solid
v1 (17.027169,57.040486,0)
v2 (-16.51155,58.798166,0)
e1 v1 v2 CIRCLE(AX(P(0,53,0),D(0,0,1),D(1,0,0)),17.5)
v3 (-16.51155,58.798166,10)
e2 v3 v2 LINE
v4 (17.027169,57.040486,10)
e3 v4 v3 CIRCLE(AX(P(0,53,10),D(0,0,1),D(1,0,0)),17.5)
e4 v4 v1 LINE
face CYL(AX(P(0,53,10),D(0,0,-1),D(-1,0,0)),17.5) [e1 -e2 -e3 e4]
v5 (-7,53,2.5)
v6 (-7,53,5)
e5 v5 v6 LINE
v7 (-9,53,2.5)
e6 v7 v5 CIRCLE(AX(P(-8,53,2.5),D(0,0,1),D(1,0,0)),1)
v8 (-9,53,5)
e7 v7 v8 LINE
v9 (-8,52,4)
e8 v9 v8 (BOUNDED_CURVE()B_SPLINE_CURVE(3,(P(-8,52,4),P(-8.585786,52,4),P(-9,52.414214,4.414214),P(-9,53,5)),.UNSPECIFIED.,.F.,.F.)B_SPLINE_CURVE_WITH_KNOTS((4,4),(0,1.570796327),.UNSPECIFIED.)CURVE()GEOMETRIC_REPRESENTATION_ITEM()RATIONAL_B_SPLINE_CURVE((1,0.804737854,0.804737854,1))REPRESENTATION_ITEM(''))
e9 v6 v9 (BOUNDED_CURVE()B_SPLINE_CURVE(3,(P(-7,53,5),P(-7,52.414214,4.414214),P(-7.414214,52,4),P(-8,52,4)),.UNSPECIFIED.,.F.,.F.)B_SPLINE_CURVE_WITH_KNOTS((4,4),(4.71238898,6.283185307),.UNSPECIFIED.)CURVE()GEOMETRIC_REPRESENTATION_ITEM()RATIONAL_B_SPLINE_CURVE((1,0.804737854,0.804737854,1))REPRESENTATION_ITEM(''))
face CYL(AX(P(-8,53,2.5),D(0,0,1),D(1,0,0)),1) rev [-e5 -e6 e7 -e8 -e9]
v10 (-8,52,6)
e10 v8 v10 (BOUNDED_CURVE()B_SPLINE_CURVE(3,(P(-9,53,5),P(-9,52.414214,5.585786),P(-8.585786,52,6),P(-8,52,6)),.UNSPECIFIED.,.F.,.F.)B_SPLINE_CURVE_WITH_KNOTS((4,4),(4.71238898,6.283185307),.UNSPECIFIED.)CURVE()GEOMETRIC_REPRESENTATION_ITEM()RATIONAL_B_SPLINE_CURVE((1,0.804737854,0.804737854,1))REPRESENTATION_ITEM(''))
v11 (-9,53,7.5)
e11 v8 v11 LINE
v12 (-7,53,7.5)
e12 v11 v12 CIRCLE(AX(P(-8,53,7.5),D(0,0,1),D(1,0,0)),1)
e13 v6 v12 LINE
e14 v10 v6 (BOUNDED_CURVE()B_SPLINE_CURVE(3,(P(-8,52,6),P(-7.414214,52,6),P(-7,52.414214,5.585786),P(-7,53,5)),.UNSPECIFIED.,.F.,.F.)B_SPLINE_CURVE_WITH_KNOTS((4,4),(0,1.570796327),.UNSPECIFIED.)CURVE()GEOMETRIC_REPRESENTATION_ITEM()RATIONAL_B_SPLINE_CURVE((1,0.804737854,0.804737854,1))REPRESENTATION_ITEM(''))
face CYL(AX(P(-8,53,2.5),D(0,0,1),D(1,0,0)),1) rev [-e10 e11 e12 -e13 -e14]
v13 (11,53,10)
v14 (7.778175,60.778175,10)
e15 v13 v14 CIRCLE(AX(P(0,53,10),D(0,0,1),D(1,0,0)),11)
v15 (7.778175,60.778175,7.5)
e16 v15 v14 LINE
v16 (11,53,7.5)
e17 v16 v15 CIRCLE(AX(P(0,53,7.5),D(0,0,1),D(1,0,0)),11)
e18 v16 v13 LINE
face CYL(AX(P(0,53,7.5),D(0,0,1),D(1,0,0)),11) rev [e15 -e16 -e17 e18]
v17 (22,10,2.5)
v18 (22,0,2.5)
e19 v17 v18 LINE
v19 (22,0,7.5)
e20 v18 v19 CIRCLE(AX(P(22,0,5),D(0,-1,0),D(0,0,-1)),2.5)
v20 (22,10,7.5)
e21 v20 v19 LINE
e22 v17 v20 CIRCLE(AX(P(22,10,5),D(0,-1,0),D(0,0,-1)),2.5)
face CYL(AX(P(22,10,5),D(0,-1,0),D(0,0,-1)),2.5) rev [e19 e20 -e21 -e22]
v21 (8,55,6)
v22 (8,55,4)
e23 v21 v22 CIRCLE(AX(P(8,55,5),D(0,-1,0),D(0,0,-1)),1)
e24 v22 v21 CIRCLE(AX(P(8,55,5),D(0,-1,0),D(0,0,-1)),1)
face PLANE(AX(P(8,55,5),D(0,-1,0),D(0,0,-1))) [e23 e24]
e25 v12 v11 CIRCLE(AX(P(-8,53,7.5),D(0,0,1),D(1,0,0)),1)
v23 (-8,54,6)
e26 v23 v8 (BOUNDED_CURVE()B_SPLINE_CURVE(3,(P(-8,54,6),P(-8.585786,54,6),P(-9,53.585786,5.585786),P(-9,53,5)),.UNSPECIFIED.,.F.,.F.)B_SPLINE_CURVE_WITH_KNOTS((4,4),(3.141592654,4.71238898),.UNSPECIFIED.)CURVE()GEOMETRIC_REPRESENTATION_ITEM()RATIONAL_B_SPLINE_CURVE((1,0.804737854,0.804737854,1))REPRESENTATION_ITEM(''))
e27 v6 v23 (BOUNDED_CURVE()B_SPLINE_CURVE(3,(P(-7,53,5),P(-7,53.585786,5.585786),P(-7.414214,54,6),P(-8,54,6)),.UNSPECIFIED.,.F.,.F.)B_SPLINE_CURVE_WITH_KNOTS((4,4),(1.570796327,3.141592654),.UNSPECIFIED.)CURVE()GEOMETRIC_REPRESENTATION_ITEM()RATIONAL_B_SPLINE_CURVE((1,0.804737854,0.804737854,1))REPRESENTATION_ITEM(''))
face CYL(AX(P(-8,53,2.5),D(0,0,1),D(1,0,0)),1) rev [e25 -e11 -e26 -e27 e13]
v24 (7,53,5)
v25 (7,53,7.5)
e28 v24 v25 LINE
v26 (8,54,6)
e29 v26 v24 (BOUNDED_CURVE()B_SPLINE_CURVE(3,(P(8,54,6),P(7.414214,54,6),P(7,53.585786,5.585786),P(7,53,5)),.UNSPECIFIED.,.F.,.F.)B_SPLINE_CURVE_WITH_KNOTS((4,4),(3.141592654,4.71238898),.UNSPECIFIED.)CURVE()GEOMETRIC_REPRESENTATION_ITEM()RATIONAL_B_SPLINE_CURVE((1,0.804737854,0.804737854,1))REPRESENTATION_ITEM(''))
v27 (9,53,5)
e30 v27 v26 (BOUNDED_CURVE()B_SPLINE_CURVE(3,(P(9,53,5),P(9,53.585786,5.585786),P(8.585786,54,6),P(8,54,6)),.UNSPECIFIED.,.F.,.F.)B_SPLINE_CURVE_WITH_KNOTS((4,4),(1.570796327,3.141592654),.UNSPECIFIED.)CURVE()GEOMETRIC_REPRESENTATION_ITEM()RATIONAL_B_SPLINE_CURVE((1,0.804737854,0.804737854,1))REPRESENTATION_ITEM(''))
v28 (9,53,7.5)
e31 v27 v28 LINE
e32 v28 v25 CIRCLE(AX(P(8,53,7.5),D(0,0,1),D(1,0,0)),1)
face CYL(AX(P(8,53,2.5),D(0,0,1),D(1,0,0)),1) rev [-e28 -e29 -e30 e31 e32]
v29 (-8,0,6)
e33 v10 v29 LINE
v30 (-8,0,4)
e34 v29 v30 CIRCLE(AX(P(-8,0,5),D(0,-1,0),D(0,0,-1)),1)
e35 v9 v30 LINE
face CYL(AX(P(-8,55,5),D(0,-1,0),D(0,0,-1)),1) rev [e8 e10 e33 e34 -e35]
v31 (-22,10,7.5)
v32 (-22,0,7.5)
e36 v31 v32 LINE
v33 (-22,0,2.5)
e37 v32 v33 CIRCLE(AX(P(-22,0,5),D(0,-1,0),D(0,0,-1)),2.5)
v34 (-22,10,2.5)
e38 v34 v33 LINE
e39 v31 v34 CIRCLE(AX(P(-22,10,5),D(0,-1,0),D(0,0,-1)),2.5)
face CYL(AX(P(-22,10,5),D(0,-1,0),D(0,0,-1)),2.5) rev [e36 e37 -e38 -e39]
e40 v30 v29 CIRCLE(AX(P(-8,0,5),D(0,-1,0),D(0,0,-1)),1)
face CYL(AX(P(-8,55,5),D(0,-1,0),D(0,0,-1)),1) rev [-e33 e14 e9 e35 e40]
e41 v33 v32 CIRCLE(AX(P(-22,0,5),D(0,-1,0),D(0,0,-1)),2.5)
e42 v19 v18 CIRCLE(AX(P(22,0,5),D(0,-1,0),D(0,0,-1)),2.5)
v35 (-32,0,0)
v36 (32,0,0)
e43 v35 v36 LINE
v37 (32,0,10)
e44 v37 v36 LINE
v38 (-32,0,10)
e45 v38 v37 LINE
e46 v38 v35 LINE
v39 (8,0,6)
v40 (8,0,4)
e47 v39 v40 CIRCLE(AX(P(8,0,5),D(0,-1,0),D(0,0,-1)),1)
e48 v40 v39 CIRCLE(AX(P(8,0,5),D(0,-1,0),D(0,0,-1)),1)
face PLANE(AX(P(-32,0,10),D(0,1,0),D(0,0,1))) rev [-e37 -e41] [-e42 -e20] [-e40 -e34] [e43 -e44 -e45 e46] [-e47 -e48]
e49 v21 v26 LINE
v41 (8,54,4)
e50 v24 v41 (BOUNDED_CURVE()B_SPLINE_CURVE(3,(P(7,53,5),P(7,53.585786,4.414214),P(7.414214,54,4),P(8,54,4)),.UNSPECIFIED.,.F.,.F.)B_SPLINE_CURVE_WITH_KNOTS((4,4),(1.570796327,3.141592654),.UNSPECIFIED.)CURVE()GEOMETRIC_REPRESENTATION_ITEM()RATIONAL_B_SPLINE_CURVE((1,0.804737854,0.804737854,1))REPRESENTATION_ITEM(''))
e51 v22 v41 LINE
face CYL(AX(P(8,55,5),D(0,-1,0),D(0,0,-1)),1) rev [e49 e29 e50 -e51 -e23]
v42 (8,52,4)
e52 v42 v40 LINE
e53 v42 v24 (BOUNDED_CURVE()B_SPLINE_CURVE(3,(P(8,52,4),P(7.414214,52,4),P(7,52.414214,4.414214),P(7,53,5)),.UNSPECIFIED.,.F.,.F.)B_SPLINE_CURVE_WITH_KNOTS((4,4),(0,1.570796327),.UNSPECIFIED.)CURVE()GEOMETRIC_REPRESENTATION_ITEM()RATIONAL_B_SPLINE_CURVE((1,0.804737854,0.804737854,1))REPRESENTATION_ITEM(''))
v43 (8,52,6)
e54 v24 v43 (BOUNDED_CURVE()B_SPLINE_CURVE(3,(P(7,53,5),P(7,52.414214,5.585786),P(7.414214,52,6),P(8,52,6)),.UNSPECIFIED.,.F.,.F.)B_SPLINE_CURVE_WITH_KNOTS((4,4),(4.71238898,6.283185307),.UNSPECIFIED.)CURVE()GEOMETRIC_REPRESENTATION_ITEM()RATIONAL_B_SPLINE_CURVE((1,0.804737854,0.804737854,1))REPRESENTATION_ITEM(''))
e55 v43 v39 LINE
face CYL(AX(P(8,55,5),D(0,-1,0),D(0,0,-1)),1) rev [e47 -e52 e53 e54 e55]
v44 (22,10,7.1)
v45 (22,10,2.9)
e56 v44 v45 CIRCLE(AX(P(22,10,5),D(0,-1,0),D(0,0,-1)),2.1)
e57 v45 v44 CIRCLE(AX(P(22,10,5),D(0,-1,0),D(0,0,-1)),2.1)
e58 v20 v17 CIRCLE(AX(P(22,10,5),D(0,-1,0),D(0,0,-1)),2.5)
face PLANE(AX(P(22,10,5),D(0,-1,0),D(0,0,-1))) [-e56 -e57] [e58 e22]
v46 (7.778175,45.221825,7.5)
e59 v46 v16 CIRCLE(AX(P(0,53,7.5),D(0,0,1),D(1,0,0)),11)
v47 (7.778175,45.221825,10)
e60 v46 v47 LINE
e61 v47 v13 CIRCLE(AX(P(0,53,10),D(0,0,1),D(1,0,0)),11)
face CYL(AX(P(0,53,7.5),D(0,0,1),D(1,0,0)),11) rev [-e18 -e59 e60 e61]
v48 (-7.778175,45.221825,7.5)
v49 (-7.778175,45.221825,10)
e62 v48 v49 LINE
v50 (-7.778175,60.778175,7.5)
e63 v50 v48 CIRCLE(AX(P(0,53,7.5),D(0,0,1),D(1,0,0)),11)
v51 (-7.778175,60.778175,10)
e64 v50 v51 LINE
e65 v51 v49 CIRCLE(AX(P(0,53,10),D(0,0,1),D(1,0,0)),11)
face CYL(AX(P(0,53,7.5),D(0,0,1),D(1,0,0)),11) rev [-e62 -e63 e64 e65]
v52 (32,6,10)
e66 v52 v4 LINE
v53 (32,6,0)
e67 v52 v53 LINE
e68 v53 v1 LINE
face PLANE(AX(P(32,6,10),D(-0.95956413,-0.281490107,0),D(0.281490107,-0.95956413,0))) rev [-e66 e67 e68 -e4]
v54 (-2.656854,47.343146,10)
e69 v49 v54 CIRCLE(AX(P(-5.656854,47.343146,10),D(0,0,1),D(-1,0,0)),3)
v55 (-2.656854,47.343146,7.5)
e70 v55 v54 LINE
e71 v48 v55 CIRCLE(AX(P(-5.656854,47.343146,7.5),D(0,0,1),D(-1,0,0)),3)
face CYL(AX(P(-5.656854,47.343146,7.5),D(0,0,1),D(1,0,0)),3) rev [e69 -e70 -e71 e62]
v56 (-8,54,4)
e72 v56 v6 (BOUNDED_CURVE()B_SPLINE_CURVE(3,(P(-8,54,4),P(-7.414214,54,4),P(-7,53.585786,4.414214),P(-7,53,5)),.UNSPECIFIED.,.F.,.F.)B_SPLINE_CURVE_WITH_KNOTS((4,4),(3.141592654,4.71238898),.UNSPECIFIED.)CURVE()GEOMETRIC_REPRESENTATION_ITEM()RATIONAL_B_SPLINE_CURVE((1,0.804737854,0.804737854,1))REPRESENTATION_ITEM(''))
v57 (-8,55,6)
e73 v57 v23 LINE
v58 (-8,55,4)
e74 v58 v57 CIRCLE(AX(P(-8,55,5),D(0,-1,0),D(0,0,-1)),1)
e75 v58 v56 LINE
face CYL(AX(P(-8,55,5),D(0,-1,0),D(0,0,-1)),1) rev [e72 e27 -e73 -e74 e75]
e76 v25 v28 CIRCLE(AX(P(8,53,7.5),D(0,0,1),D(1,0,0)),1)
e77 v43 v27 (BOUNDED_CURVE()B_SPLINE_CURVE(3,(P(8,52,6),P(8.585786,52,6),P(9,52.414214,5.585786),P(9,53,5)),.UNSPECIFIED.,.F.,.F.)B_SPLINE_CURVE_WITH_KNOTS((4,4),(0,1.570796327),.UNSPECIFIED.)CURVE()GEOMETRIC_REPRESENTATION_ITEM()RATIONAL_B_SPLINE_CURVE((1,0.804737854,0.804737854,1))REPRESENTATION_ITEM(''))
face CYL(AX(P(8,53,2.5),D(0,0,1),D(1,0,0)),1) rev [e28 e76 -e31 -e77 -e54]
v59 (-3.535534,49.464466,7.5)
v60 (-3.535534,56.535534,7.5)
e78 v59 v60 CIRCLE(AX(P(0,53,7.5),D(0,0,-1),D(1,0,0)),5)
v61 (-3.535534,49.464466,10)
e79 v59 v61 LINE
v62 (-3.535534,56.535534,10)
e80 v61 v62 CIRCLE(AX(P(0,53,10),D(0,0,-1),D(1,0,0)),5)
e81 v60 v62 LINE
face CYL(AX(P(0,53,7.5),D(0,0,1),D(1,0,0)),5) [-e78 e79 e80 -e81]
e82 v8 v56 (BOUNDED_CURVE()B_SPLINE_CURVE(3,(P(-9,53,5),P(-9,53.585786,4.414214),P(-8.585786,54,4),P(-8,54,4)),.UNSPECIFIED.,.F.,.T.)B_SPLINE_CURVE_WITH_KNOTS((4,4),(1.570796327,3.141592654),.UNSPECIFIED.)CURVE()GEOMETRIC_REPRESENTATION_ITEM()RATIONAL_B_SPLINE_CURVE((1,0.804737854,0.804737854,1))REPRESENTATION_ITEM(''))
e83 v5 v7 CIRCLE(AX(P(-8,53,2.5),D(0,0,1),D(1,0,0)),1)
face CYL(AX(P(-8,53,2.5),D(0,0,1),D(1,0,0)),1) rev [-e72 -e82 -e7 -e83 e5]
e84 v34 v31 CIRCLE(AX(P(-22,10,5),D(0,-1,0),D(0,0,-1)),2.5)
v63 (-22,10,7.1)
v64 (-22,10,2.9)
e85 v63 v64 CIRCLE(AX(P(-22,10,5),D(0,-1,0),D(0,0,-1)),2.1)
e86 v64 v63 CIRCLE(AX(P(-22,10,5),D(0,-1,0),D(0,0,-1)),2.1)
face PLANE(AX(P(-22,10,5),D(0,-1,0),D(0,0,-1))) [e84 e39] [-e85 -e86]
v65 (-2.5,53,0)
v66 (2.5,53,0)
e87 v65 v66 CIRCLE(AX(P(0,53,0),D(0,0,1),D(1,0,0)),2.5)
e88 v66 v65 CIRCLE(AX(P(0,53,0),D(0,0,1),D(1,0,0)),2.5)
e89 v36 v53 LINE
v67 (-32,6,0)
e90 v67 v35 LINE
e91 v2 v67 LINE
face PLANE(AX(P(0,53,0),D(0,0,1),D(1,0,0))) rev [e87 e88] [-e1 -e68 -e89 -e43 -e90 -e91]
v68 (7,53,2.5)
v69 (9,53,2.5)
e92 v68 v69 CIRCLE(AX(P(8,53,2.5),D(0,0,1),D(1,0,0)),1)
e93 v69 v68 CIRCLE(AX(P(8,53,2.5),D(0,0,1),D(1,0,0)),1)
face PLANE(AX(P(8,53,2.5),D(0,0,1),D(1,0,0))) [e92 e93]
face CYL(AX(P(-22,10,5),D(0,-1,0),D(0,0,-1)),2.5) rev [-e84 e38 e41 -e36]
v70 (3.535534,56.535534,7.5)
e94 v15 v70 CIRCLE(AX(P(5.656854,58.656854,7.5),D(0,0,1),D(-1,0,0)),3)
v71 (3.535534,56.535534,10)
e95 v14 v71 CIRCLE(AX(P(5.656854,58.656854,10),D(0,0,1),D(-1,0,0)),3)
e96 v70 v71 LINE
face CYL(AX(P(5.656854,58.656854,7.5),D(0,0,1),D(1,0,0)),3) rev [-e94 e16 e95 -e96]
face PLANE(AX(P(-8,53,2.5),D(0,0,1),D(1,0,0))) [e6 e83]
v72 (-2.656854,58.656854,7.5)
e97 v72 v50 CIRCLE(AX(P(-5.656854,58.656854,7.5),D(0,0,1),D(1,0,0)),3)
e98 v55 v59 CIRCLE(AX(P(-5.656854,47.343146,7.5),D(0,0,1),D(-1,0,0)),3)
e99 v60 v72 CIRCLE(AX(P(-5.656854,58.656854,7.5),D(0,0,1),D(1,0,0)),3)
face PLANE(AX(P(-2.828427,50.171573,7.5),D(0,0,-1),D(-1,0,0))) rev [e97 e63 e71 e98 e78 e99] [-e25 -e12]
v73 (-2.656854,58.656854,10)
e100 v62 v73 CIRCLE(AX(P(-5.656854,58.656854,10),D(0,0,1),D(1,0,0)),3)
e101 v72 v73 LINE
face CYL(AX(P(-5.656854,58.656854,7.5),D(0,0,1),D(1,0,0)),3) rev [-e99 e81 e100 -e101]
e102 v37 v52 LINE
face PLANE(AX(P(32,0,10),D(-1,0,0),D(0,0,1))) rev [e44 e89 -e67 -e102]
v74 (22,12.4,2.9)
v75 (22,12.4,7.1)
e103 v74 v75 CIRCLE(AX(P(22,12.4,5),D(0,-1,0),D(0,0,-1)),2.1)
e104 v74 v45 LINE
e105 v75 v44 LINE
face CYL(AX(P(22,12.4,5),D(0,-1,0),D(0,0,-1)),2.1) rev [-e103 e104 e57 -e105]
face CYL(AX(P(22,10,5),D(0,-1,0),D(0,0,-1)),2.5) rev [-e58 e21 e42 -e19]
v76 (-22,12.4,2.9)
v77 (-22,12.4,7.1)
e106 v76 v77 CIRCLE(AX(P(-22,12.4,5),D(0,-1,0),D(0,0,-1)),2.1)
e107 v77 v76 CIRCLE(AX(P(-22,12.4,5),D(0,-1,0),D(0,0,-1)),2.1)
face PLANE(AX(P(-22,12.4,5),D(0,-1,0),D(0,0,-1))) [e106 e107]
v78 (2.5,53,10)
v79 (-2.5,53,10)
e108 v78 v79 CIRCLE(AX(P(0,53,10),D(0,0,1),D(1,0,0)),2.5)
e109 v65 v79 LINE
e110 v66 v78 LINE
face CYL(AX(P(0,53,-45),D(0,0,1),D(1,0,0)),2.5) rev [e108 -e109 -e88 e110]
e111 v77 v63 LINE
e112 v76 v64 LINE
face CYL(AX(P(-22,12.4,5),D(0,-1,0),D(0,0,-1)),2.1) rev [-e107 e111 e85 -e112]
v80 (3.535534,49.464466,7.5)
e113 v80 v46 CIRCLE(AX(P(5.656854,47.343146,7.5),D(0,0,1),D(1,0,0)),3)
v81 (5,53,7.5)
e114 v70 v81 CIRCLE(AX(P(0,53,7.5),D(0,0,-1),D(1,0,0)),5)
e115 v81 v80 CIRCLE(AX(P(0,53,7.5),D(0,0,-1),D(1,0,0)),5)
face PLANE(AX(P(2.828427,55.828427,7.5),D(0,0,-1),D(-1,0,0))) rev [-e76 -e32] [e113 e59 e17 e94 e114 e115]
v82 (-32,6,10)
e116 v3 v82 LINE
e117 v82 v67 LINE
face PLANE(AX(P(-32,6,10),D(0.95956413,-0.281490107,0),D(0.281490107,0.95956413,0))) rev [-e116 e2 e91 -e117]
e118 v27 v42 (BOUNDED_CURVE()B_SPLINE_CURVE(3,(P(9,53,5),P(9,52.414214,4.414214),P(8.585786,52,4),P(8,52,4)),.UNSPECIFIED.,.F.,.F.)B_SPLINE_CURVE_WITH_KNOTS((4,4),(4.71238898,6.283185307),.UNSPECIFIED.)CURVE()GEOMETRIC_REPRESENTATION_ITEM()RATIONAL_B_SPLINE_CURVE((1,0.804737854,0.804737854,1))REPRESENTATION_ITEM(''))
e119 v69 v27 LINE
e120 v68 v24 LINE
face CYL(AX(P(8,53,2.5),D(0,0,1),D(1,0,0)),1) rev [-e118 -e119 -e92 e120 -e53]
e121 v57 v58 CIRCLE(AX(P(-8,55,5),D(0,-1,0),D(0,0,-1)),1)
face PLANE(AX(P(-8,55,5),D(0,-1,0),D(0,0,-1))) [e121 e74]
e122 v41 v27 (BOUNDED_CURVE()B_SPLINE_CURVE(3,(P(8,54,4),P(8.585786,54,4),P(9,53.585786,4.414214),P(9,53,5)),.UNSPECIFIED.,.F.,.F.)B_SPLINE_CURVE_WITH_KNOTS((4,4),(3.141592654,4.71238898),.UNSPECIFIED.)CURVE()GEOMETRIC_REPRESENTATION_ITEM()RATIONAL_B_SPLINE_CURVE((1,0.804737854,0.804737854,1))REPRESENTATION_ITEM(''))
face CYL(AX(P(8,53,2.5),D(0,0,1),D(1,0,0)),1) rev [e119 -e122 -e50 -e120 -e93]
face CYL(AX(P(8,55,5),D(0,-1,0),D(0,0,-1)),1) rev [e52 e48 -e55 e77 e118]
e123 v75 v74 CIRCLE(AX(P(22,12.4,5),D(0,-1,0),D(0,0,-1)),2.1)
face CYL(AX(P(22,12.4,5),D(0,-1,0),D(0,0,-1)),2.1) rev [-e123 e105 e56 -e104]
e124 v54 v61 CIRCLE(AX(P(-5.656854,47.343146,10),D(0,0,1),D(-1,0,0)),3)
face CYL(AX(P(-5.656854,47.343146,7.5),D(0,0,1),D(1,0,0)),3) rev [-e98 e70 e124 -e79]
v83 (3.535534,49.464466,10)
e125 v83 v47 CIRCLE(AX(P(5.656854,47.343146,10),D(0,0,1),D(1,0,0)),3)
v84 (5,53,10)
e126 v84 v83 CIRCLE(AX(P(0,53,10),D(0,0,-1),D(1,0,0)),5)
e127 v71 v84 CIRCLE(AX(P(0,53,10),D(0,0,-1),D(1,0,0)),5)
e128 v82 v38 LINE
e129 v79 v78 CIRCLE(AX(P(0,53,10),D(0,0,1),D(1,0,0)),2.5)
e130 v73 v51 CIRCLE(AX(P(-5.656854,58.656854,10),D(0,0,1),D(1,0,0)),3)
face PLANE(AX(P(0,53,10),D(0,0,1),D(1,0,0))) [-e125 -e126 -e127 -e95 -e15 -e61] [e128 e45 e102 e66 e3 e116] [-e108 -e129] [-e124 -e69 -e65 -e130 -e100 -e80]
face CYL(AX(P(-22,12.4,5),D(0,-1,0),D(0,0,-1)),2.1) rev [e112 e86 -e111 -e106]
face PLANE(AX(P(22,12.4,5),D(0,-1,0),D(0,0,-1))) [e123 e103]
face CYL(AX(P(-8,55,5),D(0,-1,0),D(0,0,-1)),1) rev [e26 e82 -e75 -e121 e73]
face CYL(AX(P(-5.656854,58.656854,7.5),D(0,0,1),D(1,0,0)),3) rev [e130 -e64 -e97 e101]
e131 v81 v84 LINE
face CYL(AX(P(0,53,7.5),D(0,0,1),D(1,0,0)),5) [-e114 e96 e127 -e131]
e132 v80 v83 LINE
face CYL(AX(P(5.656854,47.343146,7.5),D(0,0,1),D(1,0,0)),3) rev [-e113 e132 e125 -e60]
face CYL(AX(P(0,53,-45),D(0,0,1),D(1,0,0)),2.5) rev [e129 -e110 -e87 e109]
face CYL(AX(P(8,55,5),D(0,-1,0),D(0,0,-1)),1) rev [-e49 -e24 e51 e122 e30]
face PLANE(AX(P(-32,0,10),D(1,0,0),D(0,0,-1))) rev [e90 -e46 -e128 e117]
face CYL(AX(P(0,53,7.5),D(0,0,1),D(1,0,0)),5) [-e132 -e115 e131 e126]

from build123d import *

# Parameters (mm, degrees)
POST_PLATE_10MM_DEPTH       = 10
UPPER_SLOT_PROFILE_R        = 2.5
UPPER_SLOT_CUT_DEPTH        = 10
UPPER_SLOT_RELIEF_PROFILE_R = 2.1
UPPER_SLOT_RELIEF_CUT_DEPTH = 12.4
LONG_SLOT_PROFILE_R         = 1
LONG_SLOT_CUT_55_DEEP_DEPTH = 55
SHAFT_BORE_5_PROFILE_R      = 2.5
SHAFT_BORE_5_DEPTH          = 55
PIVOT_RECESS_2_5_DEEP_DEPTH = 2.5
LOWER_SLOT_PROFILE_R        = 1
LOWER_SLOT_CUT_DEPTH        = 5


with BuildPart() as part:
    # Post Plate Profile → Post Plate 10mm (new body)
    with BuildSketch(Plane.XY):
        with BuildLine():
            Line((-32, 0), (32, 0))
            Line((32, 0), (32, 6))
            Line((32, 6), (17.027168619, 57.040486211))
            ThreePointArc((17.027168619, 57.040486211), (0.915873878, 70.476017139), (-16.511549747, 58.798165653))
            Line((-16.511549747, 58.798165653), (-32, 6))
            Line((-32, 6), (-32, 0))
        make_face()
    extrude(amount=POST_PLATE_10MM_DEPTH)

    # Upper Slot Profile → Upper Slot Cut (cut)
    with BuildSketch(Plane.XZ):
        with Locations(Location((22, 5, 0), (0, 0, 270))):
            Circle(UPPER_SLOT_PROFILE_R)
        with Locations(Location((-22, 5, 0), (0, 0, 270))):
            Circle(UPPER_SLOT_PROFILE_R)
    extrude(amount=-UPPER_SLOT_CUT_DEPTH, mode=Mode.SUBTRACT)

    # Upper Slot Relief Profile → Upper Slot Relief Cut (cut)
    with BuildSketch(Plane.XZ):
        with Locations(Location((22, 5, 0), (0, 0, 270))):
            Circle(UPPER_SLOT_RELIEF_PROFILE_R)
        with Locations(Location((-22, 5, 0), (0, 0, 270))):
            Circle(UPPER_SLOT_RELIEF_PROFILE_R)
    extrude(amount=-UPPER_SLOT_RELIEF_CUT_DEPTH, mode=Mode.SUBTRACT)

    # Long Slot Profile → Long Slot Cut 55 Deep (cut)
    with BuildSketch(Plane.XZ):
        with Locations(Location((-8, 5, 0), (0, 0, 270))):
            Circle(LONG_SLOT_PROFILE_R)
        with Locations(Location((8, 5, 0), (0, 0, 270))):
            Circle(LONG_SLOT_PROFILE_R)
    extrude(amount=-LONG_SLOT_CUT_55_DEEP_DEPTH, mode=Mode.SUBTRACT)

    # Shaft Bore Ø5 Profile → Shaft Bore Ø5 (cut)
    with BuildSketch(Plane.XY.offset(10)):
        with Locations((0, 53)):
            Circle(SHAFT_BORE_5_PROFILE_R)
    extrude(amount=-SHAFT_BORE_5_DEPTH, mode=Mode.SUBTRACT)

    # Pivot Recess Profile → Pivot Recess 2.5 Deep (cut)
    with BuildSketch(Plane.XY.offset(10)):
        with BuildLine():
            ThreePointArc((-3.535533906, 56.535533906), (-5, 53), (-3.535533906, 49.464466094))
            ThreePointArc((-3.535533906, 49.464466094), (-3.535533906, 45.221825407), (-7.778174593, 45.221825407))
            ThreePointArc((-7.778174593, 45.221825407), (-11, 53), (-7.778174593, 60.778174593))
            ThreePointArc((-7.778174593, 60.778174593), (-3.535533906, 60.778174593), (-3.535533906, 56.535533906))
        make_face()
        with BuildLine():
            ThreePointArc((7.778174593, 45.221825407), (11, 53), (7.778174593, 60.778174593))
            ThreePointArc((7.778174593, 60.778174593), (3.535533906, 60.778174593), (3.535533906, 56.535533906))
            ThreePointArc((3.535533906, 56.535533906), (5, 53), (3.535533906, 49.464466094))
            ThreePointArc((3.535533906, 49.464466094), (3.535533906, 45.221825407), (7.778174593, 45.221825407))
        make_face()
    extrude(amount=-PIVOT_RECESS_2_5_DEEP_DEPTH, mode=Mode.SUBTRACT)

    # Lower Slot Profile → Lower Slot Cut (cut)
    with BuildSketch(Plane.XY.offset(7.5)):
        with Locations((8, 53)):
            Circle(LOWER_SLOT_PROFILE_R)
        with Locations((-8, 53)):
            Circle(LOWER_SLOT_PROFILE_R)
    extrude(amount=-LOWER_SLOT_CUT_DEPTH, mode=Mode.SUBTRACT)


solid = part.part
